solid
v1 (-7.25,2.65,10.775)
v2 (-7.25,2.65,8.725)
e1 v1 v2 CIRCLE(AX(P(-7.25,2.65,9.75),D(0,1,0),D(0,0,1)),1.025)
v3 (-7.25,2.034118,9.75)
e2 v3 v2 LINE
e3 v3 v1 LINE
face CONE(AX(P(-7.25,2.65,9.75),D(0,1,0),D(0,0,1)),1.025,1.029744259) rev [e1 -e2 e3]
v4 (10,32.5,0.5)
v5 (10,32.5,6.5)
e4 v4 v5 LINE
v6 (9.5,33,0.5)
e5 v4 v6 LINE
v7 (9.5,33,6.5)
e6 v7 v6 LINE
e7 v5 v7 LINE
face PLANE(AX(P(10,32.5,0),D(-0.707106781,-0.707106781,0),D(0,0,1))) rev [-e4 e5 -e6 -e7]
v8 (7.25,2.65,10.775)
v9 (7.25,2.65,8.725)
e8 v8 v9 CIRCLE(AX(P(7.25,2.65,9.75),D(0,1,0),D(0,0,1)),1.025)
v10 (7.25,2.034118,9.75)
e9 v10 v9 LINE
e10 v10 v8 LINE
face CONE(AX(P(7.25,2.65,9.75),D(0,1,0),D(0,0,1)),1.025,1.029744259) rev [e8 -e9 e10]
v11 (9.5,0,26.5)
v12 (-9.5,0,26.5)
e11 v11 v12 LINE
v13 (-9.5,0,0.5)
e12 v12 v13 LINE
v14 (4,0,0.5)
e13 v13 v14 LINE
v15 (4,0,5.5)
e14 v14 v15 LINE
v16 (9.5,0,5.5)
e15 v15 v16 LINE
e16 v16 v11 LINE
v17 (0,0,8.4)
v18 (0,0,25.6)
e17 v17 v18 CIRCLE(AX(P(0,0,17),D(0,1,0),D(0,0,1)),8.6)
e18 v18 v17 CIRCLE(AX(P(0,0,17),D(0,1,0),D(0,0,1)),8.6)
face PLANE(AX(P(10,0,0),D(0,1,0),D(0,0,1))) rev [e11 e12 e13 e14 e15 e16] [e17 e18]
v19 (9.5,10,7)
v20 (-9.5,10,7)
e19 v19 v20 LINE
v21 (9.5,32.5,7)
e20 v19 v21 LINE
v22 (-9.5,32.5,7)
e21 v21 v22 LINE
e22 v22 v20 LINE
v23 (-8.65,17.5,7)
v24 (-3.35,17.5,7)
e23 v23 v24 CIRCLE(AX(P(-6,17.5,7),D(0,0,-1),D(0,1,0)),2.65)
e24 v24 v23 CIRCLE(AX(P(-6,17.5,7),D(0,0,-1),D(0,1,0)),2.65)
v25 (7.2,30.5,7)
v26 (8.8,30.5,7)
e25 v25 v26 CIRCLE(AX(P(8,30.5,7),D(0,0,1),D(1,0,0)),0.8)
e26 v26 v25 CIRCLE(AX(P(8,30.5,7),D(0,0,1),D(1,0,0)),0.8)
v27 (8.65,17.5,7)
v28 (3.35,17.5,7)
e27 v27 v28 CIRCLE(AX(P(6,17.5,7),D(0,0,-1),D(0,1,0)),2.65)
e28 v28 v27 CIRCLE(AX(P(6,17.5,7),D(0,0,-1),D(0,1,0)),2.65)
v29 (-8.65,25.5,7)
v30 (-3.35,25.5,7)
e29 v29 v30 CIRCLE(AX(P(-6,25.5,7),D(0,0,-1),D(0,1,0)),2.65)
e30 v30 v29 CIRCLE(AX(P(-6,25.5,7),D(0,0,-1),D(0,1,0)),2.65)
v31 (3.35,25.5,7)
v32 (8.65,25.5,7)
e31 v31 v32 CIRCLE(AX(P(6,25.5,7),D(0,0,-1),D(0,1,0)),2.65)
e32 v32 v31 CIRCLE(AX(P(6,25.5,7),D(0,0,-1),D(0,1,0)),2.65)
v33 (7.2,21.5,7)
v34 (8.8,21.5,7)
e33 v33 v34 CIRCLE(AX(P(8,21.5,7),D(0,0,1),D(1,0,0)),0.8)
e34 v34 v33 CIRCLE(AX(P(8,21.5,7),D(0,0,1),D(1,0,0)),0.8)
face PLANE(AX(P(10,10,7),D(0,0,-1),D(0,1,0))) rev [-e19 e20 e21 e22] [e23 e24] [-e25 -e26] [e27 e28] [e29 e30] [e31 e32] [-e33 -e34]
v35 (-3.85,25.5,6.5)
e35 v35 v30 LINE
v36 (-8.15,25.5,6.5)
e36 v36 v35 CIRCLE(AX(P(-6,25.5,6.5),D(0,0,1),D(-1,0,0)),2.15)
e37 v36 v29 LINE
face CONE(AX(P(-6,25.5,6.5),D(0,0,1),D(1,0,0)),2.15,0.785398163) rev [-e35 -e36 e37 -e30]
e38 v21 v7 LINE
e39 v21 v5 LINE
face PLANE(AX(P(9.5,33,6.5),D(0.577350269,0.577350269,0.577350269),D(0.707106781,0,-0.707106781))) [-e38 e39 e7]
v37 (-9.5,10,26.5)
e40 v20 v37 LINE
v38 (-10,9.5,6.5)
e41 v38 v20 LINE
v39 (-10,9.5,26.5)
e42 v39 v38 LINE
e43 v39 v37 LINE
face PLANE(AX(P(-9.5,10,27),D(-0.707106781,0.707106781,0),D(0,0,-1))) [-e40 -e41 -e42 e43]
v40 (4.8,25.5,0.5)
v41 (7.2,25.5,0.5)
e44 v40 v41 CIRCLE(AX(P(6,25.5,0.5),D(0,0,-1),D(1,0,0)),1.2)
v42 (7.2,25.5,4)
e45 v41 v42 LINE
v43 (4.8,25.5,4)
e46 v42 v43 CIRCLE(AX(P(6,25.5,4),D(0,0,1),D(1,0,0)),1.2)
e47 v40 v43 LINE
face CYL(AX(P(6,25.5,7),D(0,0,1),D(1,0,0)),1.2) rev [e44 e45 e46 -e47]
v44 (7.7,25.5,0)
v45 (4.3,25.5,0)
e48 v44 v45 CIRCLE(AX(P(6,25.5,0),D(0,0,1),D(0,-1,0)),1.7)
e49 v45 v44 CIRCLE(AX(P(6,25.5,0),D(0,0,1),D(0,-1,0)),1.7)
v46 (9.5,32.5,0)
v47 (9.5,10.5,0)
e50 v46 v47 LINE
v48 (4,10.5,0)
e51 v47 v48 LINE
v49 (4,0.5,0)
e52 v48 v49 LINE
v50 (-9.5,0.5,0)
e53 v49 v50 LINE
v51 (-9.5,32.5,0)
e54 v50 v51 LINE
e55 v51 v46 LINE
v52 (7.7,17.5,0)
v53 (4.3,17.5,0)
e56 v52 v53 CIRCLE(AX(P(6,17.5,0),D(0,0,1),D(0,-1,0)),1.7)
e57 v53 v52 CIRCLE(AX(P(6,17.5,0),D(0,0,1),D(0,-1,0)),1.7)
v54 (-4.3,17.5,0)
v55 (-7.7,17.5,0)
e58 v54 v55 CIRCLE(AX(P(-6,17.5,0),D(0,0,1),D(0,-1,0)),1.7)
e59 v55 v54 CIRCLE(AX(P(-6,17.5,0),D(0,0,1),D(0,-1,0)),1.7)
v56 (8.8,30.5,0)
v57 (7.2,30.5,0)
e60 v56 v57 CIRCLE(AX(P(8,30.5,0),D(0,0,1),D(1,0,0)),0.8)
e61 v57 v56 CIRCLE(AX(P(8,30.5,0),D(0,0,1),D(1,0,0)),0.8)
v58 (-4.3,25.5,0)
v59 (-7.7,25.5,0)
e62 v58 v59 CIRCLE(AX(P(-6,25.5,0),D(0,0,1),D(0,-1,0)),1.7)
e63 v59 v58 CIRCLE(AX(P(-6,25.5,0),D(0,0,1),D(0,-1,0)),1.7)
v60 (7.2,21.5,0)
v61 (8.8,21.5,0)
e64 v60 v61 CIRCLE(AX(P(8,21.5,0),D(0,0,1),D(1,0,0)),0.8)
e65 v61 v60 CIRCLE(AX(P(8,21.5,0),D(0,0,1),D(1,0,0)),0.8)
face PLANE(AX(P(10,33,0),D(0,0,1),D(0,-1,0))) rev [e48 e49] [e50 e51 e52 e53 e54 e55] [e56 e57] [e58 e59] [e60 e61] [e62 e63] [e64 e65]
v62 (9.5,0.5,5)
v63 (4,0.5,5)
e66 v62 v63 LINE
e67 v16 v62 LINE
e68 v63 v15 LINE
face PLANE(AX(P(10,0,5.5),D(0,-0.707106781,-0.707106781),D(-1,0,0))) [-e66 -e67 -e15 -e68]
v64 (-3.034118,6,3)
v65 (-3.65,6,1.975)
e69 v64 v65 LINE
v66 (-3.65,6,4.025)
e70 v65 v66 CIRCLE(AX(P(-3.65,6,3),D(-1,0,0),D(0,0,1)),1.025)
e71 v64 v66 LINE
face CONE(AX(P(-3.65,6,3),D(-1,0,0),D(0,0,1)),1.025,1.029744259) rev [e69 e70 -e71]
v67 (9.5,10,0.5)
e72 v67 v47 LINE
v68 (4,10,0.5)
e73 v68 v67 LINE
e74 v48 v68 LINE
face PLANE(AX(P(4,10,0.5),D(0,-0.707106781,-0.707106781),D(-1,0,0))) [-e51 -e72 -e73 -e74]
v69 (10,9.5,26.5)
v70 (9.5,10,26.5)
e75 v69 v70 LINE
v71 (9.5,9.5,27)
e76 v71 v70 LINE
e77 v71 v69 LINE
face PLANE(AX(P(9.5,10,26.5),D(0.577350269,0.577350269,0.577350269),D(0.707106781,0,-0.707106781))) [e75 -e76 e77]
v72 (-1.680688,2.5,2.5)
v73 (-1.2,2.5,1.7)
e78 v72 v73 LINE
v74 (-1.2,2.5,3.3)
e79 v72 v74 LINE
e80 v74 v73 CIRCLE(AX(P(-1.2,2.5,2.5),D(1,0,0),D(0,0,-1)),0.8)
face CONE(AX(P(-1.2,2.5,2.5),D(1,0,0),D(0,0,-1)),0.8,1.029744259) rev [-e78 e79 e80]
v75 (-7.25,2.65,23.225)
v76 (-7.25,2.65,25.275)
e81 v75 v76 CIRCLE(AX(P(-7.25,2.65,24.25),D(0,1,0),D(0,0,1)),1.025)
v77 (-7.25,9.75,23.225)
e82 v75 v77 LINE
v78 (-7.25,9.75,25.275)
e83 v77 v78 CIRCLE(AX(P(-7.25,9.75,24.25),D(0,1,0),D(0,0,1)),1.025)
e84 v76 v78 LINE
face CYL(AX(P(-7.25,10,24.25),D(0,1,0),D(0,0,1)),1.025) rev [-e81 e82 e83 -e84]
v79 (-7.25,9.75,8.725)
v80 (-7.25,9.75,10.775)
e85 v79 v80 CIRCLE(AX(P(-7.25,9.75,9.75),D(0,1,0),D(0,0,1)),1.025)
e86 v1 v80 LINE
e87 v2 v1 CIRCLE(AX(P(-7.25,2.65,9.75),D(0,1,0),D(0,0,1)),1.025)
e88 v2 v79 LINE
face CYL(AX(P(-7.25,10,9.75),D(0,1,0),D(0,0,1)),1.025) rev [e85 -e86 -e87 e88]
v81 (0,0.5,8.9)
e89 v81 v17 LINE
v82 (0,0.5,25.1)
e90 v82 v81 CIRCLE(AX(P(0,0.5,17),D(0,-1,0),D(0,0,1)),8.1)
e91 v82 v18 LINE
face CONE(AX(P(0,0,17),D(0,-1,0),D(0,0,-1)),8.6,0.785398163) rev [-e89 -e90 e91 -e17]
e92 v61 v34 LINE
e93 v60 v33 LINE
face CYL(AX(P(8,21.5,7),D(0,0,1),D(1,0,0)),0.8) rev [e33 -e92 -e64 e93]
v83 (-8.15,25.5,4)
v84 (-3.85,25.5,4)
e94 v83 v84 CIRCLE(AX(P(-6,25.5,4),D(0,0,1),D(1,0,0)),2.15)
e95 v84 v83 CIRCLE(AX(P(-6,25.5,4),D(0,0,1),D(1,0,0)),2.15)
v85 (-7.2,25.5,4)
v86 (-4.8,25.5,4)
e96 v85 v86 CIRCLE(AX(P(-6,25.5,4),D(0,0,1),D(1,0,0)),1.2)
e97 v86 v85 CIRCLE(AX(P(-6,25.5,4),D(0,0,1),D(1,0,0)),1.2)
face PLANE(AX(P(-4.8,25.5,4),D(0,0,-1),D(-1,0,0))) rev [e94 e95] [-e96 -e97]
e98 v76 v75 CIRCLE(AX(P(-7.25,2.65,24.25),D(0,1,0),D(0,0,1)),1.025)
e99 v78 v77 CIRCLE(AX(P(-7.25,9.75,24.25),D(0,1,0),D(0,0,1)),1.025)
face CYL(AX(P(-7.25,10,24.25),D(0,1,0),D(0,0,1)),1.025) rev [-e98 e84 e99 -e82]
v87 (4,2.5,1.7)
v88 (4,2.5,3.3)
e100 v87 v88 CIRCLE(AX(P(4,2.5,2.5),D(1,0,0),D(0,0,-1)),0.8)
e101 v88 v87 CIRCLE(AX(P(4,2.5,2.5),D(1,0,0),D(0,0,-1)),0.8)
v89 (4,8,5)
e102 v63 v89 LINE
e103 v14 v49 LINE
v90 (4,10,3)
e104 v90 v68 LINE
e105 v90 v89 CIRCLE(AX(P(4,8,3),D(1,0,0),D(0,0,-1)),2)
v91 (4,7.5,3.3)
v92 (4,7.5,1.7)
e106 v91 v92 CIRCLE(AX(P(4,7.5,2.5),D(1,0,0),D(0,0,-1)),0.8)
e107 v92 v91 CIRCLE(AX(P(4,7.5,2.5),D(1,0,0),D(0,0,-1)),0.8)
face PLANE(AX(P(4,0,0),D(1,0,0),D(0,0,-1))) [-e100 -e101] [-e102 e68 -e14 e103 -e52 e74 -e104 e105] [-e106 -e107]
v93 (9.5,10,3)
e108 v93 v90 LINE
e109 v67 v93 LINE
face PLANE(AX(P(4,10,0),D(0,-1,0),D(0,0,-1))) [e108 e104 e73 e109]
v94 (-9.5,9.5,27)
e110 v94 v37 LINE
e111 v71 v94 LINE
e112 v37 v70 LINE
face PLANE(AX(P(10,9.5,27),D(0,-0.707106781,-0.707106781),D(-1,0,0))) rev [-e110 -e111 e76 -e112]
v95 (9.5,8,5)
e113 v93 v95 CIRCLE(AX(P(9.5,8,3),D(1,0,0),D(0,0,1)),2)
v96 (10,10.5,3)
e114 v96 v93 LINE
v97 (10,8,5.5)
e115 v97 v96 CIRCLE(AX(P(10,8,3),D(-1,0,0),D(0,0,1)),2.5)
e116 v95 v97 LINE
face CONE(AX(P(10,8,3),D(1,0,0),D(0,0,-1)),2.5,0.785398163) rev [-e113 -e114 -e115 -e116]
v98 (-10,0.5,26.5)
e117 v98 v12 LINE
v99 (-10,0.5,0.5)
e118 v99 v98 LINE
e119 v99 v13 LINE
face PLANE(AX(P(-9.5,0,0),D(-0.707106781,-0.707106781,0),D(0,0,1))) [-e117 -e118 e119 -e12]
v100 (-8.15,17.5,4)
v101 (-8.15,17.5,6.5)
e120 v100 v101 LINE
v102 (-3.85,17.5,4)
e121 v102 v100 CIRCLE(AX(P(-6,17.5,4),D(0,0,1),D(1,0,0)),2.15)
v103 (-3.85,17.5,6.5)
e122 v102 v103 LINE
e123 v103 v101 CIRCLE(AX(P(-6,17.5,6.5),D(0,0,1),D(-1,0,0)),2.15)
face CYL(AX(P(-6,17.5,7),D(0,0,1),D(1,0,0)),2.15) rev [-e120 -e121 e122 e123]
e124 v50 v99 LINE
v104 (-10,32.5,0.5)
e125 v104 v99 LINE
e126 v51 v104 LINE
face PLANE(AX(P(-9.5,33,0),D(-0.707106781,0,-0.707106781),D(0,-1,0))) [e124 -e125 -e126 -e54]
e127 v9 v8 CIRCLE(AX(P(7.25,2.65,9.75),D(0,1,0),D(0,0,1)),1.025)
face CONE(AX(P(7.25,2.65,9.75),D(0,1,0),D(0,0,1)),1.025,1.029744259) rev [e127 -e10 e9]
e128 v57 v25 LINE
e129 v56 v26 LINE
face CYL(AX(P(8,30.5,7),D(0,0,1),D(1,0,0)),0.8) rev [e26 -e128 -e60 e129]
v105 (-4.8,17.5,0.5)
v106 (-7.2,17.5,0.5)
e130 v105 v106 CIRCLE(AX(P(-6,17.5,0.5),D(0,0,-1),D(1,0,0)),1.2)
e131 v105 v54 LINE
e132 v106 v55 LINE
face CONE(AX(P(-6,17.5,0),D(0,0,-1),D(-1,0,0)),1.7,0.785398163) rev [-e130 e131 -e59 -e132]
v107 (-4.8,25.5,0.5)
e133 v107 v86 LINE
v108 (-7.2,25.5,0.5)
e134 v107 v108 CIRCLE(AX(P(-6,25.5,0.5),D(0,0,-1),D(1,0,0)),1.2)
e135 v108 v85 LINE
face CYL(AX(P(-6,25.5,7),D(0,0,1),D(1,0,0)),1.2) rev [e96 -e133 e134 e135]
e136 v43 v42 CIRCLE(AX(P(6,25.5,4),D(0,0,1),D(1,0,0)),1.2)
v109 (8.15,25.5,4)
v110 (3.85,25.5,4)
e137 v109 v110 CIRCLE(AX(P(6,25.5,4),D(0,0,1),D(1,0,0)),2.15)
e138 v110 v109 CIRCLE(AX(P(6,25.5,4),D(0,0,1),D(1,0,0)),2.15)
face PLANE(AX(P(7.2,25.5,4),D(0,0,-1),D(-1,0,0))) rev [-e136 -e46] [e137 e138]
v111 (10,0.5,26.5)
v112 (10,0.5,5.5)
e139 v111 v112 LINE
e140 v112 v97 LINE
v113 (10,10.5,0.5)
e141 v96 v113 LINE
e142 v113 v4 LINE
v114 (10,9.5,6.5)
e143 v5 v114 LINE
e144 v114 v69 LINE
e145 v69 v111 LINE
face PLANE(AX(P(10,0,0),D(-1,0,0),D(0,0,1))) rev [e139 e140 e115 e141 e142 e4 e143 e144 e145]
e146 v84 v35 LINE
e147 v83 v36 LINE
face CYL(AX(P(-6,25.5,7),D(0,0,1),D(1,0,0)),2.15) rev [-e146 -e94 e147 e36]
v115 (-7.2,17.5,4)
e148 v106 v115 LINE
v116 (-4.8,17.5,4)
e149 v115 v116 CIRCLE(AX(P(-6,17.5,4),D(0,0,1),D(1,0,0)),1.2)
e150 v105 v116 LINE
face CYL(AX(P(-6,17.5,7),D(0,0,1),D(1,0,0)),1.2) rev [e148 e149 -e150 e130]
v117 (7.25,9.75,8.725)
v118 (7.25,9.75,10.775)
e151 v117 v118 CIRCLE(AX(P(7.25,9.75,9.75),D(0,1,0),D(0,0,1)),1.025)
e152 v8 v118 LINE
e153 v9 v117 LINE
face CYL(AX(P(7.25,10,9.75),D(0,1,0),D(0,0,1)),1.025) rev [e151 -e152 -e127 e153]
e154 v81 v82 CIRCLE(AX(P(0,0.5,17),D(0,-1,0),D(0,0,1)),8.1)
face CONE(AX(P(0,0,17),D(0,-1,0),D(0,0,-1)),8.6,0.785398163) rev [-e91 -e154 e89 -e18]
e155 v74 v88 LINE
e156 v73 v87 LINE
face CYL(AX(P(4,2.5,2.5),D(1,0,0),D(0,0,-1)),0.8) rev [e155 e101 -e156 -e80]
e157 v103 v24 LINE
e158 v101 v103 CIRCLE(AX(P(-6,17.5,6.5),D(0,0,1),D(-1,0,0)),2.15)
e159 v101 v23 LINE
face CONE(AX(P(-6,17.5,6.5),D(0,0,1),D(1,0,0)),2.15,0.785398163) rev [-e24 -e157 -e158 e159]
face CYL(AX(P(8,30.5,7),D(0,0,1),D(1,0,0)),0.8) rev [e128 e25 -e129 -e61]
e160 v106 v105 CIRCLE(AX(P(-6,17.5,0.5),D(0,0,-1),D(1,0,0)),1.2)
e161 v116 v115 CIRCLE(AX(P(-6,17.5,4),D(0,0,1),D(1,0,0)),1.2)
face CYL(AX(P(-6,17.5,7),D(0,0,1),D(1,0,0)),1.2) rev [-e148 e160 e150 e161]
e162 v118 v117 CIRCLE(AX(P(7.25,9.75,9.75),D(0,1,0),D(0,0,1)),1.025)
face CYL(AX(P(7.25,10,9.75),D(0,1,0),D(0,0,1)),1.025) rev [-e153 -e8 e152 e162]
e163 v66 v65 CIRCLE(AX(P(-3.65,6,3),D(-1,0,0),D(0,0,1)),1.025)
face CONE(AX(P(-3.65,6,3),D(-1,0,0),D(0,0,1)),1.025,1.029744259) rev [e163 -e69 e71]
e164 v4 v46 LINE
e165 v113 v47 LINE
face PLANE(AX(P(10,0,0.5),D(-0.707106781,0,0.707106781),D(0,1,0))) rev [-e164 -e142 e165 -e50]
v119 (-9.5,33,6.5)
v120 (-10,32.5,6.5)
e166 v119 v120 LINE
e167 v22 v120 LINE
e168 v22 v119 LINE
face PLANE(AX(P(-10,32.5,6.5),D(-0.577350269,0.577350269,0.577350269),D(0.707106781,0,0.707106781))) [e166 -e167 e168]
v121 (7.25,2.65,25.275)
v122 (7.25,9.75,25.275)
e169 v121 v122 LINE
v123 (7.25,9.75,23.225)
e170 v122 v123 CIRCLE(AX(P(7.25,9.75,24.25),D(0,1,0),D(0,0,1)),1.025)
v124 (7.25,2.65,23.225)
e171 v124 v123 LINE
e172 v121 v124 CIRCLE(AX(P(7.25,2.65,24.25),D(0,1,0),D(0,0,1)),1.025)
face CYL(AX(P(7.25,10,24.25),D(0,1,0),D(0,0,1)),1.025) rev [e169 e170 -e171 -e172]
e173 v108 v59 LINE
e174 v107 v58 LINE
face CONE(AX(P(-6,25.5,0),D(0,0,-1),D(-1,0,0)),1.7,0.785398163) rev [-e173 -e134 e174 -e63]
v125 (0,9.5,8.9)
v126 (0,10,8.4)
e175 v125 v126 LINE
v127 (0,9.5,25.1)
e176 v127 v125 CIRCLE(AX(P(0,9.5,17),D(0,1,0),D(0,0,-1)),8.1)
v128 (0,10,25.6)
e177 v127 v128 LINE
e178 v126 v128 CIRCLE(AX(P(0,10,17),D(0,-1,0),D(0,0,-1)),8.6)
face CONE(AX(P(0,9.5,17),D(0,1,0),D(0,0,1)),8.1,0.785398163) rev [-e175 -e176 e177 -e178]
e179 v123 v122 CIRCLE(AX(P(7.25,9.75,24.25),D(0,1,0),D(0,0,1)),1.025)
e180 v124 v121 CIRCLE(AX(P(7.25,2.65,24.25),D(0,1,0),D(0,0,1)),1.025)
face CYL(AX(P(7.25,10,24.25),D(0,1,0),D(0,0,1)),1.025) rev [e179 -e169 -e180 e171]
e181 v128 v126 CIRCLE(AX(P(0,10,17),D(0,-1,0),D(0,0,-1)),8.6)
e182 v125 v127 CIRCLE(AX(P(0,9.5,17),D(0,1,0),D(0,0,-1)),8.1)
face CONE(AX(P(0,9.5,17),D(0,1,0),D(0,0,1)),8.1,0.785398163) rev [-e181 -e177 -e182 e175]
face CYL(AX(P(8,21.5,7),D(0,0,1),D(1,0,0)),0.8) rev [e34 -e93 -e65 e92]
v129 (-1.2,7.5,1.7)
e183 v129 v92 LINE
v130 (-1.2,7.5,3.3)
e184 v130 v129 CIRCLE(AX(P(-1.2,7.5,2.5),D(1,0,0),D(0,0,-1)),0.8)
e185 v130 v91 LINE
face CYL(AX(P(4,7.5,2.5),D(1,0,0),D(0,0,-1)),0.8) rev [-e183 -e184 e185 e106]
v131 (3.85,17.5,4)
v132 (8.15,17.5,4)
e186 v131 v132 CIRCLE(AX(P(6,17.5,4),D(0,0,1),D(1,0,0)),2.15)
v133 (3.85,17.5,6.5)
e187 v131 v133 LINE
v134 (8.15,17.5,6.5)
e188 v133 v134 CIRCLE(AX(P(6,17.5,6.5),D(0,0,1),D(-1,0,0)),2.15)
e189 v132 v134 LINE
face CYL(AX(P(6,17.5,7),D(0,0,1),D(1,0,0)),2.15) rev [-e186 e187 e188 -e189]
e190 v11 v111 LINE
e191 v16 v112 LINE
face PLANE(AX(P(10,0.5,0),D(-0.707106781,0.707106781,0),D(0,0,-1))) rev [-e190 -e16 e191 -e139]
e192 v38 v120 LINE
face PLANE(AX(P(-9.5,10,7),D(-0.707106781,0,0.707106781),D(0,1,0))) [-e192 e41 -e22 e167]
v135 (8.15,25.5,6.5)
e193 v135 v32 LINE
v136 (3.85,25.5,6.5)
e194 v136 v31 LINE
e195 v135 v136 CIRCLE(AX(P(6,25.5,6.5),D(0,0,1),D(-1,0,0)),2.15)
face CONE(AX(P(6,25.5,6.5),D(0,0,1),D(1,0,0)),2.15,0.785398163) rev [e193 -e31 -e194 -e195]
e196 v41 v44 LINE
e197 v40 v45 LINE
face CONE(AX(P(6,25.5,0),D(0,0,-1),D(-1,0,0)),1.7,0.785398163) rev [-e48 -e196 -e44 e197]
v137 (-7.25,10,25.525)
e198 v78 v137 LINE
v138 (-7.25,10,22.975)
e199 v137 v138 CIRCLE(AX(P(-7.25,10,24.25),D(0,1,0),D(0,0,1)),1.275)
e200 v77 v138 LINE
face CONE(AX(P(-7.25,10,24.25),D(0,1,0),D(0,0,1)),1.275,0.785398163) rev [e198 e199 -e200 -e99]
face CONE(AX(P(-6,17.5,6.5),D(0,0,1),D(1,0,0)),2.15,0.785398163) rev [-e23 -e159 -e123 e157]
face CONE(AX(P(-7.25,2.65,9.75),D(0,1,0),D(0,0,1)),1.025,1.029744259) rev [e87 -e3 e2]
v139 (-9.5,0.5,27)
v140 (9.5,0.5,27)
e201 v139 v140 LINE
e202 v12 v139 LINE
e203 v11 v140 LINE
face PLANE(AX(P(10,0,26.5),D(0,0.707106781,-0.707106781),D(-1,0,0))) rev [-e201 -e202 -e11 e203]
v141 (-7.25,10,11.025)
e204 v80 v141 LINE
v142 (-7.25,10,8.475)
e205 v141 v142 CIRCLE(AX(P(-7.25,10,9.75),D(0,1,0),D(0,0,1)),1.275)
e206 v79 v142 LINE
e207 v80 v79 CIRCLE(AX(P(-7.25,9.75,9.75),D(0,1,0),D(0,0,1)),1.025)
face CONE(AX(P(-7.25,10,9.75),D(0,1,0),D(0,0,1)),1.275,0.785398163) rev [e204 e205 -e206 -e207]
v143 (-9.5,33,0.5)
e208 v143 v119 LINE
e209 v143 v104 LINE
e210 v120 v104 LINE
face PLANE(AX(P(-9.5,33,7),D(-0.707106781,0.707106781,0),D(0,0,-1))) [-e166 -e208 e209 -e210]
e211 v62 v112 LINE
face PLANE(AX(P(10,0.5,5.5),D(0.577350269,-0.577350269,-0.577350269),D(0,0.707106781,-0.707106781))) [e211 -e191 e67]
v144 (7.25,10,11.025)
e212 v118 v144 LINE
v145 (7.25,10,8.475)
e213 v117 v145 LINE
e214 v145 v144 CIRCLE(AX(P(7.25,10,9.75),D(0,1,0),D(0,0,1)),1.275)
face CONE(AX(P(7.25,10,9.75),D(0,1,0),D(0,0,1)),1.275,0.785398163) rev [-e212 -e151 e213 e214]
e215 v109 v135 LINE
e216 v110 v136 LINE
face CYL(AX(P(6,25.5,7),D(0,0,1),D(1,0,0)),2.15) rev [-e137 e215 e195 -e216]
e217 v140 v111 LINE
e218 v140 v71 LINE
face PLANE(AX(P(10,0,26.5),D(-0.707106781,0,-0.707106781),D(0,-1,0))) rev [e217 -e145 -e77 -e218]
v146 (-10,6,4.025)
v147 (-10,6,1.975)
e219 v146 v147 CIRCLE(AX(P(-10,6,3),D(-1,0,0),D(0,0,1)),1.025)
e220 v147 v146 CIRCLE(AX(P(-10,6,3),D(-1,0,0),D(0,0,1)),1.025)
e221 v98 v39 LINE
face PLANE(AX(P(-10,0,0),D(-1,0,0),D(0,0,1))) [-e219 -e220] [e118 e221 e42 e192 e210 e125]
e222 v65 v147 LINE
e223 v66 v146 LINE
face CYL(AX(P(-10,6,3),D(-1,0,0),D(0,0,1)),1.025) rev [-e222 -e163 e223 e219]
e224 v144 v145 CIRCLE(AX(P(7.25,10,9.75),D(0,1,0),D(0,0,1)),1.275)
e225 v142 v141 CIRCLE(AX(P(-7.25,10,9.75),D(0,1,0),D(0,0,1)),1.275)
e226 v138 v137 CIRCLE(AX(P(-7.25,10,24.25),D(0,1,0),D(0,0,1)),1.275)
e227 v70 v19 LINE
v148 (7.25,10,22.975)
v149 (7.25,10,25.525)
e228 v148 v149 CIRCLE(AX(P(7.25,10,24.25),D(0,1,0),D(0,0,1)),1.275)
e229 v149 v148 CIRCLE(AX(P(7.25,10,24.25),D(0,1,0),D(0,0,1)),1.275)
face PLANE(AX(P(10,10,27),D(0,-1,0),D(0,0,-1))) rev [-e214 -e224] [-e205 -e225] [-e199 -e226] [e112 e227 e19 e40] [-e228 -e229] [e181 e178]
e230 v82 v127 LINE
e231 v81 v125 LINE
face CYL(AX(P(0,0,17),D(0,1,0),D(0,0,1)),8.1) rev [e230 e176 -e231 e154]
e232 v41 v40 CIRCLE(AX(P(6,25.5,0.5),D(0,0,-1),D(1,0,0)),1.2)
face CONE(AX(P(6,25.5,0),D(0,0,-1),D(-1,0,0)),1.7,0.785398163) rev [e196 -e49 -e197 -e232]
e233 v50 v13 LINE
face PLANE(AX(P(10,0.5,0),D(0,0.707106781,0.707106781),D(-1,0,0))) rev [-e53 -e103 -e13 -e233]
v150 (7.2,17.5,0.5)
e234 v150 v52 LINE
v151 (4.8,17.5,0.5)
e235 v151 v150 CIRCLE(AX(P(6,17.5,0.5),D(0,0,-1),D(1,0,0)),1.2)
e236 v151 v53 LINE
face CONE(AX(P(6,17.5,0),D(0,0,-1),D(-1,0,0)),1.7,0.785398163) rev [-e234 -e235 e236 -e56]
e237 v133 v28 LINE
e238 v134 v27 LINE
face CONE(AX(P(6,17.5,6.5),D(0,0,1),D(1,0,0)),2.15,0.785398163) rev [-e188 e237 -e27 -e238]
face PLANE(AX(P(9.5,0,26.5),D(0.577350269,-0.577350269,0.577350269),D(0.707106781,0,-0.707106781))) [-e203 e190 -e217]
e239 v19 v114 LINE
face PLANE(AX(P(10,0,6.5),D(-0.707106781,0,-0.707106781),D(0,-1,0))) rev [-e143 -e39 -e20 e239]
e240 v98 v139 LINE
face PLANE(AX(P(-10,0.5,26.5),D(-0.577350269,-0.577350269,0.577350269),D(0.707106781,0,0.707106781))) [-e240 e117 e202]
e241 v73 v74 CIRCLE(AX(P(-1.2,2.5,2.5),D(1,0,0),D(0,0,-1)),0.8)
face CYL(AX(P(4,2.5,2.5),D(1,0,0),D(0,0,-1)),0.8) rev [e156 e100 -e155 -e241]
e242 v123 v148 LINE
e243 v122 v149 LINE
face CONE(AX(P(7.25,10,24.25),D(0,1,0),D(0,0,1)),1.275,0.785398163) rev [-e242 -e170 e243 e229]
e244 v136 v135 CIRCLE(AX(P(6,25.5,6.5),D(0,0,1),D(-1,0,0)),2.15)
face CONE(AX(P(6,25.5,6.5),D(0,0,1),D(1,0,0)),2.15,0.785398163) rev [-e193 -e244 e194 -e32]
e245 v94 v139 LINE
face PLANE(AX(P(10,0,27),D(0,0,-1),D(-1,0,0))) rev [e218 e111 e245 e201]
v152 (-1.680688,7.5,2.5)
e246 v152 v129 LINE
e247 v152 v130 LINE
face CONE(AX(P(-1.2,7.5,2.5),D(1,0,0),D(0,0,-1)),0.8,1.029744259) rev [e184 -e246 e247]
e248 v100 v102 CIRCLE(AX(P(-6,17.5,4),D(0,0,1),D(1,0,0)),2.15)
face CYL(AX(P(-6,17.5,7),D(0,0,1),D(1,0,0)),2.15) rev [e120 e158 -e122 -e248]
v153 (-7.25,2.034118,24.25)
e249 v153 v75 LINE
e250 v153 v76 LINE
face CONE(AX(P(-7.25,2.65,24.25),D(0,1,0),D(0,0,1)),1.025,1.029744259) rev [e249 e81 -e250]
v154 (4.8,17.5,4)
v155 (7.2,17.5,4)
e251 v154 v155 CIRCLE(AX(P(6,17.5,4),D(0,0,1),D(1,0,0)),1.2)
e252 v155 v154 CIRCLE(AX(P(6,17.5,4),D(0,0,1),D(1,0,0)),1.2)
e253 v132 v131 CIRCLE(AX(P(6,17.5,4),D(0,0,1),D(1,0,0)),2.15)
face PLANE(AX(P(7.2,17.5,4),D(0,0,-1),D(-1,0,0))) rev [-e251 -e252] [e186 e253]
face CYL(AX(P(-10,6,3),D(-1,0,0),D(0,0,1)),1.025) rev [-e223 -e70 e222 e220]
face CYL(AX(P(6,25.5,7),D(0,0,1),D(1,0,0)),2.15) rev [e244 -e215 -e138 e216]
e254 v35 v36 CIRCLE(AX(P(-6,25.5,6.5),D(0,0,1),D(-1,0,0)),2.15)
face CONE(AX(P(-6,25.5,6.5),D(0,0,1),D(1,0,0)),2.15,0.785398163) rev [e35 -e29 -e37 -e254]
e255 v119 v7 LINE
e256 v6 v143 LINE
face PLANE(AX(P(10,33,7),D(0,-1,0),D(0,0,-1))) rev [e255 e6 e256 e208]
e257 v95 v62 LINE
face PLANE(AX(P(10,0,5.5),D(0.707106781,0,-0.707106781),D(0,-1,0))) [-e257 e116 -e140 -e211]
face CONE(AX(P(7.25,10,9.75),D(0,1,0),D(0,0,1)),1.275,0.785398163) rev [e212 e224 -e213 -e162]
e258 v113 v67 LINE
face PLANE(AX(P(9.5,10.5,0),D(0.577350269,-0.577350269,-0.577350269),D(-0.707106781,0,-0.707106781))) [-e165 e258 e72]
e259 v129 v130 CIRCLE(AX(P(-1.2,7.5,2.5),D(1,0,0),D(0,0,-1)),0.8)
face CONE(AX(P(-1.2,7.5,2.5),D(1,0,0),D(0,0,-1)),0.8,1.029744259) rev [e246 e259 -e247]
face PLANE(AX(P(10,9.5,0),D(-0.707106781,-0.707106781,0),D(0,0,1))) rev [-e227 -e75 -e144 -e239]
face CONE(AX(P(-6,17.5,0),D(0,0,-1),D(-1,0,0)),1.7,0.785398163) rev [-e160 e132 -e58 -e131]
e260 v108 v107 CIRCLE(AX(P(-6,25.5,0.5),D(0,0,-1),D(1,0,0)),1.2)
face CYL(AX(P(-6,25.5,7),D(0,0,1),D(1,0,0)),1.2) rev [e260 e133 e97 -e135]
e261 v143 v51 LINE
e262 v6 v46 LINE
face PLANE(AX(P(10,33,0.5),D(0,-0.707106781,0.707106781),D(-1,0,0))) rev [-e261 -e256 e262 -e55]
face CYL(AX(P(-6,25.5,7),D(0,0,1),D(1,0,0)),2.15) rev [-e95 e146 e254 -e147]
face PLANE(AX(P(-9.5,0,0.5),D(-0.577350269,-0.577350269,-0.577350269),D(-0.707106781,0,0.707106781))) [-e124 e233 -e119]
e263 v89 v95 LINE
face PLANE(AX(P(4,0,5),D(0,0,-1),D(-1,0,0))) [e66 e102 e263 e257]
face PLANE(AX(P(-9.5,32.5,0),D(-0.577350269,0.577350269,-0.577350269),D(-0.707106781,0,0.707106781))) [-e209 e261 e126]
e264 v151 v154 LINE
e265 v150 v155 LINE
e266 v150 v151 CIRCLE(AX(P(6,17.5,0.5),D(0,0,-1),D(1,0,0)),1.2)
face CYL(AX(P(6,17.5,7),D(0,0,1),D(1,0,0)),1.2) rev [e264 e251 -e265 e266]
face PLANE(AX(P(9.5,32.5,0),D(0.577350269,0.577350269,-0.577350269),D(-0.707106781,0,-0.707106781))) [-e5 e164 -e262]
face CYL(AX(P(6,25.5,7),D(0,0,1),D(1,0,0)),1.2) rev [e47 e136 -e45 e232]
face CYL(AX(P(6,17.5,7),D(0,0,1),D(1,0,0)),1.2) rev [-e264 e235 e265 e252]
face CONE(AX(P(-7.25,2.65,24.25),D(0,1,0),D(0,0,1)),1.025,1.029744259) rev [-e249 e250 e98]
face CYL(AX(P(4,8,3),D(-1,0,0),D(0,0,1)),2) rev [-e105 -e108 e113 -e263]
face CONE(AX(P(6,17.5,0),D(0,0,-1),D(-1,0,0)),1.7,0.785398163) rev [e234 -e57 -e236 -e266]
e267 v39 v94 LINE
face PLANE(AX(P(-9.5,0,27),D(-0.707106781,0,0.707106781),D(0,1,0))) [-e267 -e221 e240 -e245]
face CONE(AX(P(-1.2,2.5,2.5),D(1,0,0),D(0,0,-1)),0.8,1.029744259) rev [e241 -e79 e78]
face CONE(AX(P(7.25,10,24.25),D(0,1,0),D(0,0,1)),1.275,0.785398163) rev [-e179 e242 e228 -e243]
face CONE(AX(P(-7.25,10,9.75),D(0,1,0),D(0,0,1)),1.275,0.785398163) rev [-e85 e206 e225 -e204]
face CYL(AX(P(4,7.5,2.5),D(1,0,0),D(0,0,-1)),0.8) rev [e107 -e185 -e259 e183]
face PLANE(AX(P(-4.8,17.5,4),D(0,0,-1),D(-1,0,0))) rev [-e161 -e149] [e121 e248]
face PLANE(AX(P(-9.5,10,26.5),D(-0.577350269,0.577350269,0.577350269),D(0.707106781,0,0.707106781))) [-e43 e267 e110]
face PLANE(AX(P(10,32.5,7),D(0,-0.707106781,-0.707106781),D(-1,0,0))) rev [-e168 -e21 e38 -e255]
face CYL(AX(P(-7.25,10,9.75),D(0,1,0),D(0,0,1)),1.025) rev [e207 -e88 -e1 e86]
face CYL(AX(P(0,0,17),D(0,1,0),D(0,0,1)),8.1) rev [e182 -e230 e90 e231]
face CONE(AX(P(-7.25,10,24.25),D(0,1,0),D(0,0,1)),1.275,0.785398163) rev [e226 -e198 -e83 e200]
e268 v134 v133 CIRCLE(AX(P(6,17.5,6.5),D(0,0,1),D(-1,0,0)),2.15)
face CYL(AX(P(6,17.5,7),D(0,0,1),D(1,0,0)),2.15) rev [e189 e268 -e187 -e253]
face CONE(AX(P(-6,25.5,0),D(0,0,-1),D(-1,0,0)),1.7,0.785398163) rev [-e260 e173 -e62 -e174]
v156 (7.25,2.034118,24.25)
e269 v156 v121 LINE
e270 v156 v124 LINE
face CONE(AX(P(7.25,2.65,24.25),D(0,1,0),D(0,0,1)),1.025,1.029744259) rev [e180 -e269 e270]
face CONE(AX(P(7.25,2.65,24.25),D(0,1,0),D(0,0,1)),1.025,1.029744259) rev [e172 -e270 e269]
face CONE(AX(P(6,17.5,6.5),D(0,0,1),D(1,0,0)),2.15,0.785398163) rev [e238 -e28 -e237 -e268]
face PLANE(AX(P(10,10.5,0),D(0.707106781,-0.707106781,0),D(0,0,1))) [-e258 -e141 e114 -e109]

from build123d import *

# Parameters (mm, degrees)
BOSS_EXTRUDE1_DEPTH                                = 10
SKETCH2_R                                          = 8.1
CUT_EXTRUDE1_DEPTH                                 = 10
M2_5_TAPPED_HOLE1_D                                = 2.05
M2_5_TAPPED_HOLE1_DEPTH                            = 7.35
M2_5_TAPPED_HOLE1_CSINK_D                          = 2.55
M2_5_TAPPED_HOLE1_CSINK_ANGLE                      = 90
M2_5_TAPPED_HOLE1_TIP                              = 0.615882135
HOLE_SIZE_SOCKET_HEAD_CAP_SCREW_TYPE_0_D           = 2.4
HOLE_SIZE_SOCKET_HEAD_CAP_SCREW_TYPE_0_CBORE_D     = 4.3
HOLE_SIZE_SOCKET_HEAD_CAP_SCREW_TYPE_0_CBORE_DEPTH = 3
SKETCH9_W                                          = 5
SKETCH9_H                                          = 10
CUT_EXTRUDE4_DEPTH                                 = 6
M2_TAPPED_HOLE1_D                                  = 1.6
M2_TAPPED_HOLE1_DEPTH                              = 5.2
M2_TAPPED_HOLE1_TIP                                = 0.480688495
FILLET1_R                                          = 2
CHAMFER1_SIZE                                      = 0.5
M2_5_TAPPED_HOLE2_D                                = 2.05
M2_5_TAPPED_HOLE2_DEPTH                            = 6.35
M2_5_TAPPED_HOLE2_TIP                              = 0.615882135
M2_TAPPED_HOLE2_D                                  = 1.6


with BuildPart() as part:
    # Sketch1 → Boss-Extrude1 (new, symmetric)
    with BuildSketch(Plane(origin=(0, 0, 0), x_dir=(0, 0, -1), z_dir=(1, 0, 0))):
        Polygon((0, 33), (0, 0), (-27, 0), (-27, 10), (-7, 10), (-7, 33), align=None)
    extrude(amount=BOSS_EXTRUDE1_DEPTH, both=True)

    # Sketch2 → Cut-Extrude1 (cut)
    with BuildSketch(Plane(origin=(0, 10, 0), x_dir=(1, 0, 0), z_dir=(0, 1, 0))):
        with Locations(Location((0, -17, 0), (0, 0, 270))):
            Circle(SKETCH2_R)
    extrude(amount=-CUT_EXTRUDE1_DEPTH, mode=Mode.SUBTRACT)

    # M2.5 Tapped Hole1
    with Locations(Plane(origin=(0, 10, 0), x_dir=(1, 0, 0), z_dir=(0, 1, 0))):
        with Locations((-7.25, -9.75), (-7.25, -24.25), (7.25, -24.25), (7.25, -9.75)):
            CounterSinkHole(M2_5_TAPPED_HOLE1_D / 2, M2_5_TAPPED_HOLE1_CSINK_D / 2, depth=M2_5_TAPPED_HOLE1_DEPTH, counter_sink_angle=M2_5_TAPPED_HOLE1_CSINK_ANGLE)
            with Locations((0, 0, -(M2_5_TAPPED_HOLE1_DEPTH + M2_5_TAPPED_HOLE1_TIP / 2))):  # 118° drill point
                Cone(0, M2_5_TAPPED_HOLE1_D / 2, M2_5_TAPPED_HOLE1_TIP, mode=Mode.SUBTRACT)

    # Hole size socket head cap screw type 0 (through all)
    with Locations(Plane.XY.offset(7)):
        with Locations((-6, 25.5), (6, 25.5), (6, 17.5), (-6, 17.5)):
            CounterBoreHole(HOLE_SIZE_SOCKET_HEAD_CAP_SCREW_TYPE_0_D / 2, HOLE_SIZE_SOCKET_HEAD_CAP_SCREW_TYPE_0_CBORE_D / 2, HOLE_SIZE_SOCKET_HEAD_CAP_SCREW_TYPE_0_CBORE_DEPTH)

    # Sketch9 → Cut-Extrude4 (cut)
    with BuildSketch(Plane.ZY.offset(-10)):
        with Locations((2.5, 5)):
            Rectangle(SKETCH9_W, SKETCH9_H)
    extrude(amount=CUT_EXTRUDE4_DEPTH, mode=Mode.SUBTRACT)

    # M2 Tapped Hole1
    with Locations(Plane(origin=(4, 0, 0), x_dir=(0, 0, -1), z_dir=(1, 0, 0))):
        with Locations((-2.5, 7.5), (-2.5, 2.5)):
            Hole(M2_TAPPED_HOLE1_D / 2, depth=M2_TAPPED_HOLE1_DEPTH)
            with Locations((0, 0, -(M2_TAPPED_HOLE1_DEPTH + M2_TAPPED_HOLE1_TIP / 2))):  # 118° drill point
                Cone(0, M2_TAPPED_HOLE1_D / 2, M2_TAPPED_HOLE1_TIP, mode=Mode.SUBTRACT)

    # Fillet1
    fillet1_edges = [part.edges().sort_by_distance(p)[0] for p in [
        (7, 10, 5),
    ]]
    fillet(fillet1_edges, radius=FILLET1_R)

    # Chamfer1
    chamfer1_edges = [part.edges().sort_by_distance(p)[0] for p in [
        (10, 10, 1.5),
        (10, 9.414213562, 4.414213562),
        (0, 33, 0),
        (0, 0, 27),
        (0, 10, 27),
        (0, 33, 7),
        (10, 10, 17),
        (10, 5, 27),
        (0, 0, 8.9),
        (0, 10, 8.9),
        (10, 0, 16),
        (10, 33, 3.5),
        (-8.15, 17.5, 7),
        (-4.8, 17.5, 0),
        (3.85, 17.5, 7),
        (7.2, 17.5, 0),
        (3.85, 25.5, 7),
        (7.2, 25.5, 0),
        (-10, 16.5, 0),
        (-8.15, 25.5, 7),
        (-4.8, 25.5, 0),
        (-10, 0, 13.5),
        (-10, 5, 27),
        (10, 21.5, 0),
        (-10, 10, 17),
        (-3, 0, 0),
        (7, 10, 0),
        (10, 4, 5),
        (-10, 21.5, 7),
        (7, 0, 5),
        (-10, 33, 3.5),
        (10, 21.5, 7),
    ]]
    chamfer(chamfer1_edges, length=CHAMFER1_SIZE)

    # M2.5 Tapped Hole2
    with Locations(Plane.ZY.offset(10)):
        with Locations((3, 6)):
            Hole(M2_5_TAPPED_HOLE2_D / 2, depth=M2_5_TAPPED_HOLE2_DEPTH)
            with Locations((0, 0, -(M2_5_TAPPED_HOLE2_DEPTH + M2_5_TAPPED_HOLE2_TIP / 2))):  # 118° drill point
                Cone(0, M2_5_TAPPED_HOLE2_D / 2, M2_5_TAPPED_HOLE2_TIP, mode=Mode.SUBTRACT)

    # M2 Tapped Hole2 (through all)
    with Locations(Plane.XY.offset(7)):
        with Locations((8, 30.5), (8, 21.5)):
            Hole(M2_TAPPED_HOLE2_D / 2)


solid = part.part
